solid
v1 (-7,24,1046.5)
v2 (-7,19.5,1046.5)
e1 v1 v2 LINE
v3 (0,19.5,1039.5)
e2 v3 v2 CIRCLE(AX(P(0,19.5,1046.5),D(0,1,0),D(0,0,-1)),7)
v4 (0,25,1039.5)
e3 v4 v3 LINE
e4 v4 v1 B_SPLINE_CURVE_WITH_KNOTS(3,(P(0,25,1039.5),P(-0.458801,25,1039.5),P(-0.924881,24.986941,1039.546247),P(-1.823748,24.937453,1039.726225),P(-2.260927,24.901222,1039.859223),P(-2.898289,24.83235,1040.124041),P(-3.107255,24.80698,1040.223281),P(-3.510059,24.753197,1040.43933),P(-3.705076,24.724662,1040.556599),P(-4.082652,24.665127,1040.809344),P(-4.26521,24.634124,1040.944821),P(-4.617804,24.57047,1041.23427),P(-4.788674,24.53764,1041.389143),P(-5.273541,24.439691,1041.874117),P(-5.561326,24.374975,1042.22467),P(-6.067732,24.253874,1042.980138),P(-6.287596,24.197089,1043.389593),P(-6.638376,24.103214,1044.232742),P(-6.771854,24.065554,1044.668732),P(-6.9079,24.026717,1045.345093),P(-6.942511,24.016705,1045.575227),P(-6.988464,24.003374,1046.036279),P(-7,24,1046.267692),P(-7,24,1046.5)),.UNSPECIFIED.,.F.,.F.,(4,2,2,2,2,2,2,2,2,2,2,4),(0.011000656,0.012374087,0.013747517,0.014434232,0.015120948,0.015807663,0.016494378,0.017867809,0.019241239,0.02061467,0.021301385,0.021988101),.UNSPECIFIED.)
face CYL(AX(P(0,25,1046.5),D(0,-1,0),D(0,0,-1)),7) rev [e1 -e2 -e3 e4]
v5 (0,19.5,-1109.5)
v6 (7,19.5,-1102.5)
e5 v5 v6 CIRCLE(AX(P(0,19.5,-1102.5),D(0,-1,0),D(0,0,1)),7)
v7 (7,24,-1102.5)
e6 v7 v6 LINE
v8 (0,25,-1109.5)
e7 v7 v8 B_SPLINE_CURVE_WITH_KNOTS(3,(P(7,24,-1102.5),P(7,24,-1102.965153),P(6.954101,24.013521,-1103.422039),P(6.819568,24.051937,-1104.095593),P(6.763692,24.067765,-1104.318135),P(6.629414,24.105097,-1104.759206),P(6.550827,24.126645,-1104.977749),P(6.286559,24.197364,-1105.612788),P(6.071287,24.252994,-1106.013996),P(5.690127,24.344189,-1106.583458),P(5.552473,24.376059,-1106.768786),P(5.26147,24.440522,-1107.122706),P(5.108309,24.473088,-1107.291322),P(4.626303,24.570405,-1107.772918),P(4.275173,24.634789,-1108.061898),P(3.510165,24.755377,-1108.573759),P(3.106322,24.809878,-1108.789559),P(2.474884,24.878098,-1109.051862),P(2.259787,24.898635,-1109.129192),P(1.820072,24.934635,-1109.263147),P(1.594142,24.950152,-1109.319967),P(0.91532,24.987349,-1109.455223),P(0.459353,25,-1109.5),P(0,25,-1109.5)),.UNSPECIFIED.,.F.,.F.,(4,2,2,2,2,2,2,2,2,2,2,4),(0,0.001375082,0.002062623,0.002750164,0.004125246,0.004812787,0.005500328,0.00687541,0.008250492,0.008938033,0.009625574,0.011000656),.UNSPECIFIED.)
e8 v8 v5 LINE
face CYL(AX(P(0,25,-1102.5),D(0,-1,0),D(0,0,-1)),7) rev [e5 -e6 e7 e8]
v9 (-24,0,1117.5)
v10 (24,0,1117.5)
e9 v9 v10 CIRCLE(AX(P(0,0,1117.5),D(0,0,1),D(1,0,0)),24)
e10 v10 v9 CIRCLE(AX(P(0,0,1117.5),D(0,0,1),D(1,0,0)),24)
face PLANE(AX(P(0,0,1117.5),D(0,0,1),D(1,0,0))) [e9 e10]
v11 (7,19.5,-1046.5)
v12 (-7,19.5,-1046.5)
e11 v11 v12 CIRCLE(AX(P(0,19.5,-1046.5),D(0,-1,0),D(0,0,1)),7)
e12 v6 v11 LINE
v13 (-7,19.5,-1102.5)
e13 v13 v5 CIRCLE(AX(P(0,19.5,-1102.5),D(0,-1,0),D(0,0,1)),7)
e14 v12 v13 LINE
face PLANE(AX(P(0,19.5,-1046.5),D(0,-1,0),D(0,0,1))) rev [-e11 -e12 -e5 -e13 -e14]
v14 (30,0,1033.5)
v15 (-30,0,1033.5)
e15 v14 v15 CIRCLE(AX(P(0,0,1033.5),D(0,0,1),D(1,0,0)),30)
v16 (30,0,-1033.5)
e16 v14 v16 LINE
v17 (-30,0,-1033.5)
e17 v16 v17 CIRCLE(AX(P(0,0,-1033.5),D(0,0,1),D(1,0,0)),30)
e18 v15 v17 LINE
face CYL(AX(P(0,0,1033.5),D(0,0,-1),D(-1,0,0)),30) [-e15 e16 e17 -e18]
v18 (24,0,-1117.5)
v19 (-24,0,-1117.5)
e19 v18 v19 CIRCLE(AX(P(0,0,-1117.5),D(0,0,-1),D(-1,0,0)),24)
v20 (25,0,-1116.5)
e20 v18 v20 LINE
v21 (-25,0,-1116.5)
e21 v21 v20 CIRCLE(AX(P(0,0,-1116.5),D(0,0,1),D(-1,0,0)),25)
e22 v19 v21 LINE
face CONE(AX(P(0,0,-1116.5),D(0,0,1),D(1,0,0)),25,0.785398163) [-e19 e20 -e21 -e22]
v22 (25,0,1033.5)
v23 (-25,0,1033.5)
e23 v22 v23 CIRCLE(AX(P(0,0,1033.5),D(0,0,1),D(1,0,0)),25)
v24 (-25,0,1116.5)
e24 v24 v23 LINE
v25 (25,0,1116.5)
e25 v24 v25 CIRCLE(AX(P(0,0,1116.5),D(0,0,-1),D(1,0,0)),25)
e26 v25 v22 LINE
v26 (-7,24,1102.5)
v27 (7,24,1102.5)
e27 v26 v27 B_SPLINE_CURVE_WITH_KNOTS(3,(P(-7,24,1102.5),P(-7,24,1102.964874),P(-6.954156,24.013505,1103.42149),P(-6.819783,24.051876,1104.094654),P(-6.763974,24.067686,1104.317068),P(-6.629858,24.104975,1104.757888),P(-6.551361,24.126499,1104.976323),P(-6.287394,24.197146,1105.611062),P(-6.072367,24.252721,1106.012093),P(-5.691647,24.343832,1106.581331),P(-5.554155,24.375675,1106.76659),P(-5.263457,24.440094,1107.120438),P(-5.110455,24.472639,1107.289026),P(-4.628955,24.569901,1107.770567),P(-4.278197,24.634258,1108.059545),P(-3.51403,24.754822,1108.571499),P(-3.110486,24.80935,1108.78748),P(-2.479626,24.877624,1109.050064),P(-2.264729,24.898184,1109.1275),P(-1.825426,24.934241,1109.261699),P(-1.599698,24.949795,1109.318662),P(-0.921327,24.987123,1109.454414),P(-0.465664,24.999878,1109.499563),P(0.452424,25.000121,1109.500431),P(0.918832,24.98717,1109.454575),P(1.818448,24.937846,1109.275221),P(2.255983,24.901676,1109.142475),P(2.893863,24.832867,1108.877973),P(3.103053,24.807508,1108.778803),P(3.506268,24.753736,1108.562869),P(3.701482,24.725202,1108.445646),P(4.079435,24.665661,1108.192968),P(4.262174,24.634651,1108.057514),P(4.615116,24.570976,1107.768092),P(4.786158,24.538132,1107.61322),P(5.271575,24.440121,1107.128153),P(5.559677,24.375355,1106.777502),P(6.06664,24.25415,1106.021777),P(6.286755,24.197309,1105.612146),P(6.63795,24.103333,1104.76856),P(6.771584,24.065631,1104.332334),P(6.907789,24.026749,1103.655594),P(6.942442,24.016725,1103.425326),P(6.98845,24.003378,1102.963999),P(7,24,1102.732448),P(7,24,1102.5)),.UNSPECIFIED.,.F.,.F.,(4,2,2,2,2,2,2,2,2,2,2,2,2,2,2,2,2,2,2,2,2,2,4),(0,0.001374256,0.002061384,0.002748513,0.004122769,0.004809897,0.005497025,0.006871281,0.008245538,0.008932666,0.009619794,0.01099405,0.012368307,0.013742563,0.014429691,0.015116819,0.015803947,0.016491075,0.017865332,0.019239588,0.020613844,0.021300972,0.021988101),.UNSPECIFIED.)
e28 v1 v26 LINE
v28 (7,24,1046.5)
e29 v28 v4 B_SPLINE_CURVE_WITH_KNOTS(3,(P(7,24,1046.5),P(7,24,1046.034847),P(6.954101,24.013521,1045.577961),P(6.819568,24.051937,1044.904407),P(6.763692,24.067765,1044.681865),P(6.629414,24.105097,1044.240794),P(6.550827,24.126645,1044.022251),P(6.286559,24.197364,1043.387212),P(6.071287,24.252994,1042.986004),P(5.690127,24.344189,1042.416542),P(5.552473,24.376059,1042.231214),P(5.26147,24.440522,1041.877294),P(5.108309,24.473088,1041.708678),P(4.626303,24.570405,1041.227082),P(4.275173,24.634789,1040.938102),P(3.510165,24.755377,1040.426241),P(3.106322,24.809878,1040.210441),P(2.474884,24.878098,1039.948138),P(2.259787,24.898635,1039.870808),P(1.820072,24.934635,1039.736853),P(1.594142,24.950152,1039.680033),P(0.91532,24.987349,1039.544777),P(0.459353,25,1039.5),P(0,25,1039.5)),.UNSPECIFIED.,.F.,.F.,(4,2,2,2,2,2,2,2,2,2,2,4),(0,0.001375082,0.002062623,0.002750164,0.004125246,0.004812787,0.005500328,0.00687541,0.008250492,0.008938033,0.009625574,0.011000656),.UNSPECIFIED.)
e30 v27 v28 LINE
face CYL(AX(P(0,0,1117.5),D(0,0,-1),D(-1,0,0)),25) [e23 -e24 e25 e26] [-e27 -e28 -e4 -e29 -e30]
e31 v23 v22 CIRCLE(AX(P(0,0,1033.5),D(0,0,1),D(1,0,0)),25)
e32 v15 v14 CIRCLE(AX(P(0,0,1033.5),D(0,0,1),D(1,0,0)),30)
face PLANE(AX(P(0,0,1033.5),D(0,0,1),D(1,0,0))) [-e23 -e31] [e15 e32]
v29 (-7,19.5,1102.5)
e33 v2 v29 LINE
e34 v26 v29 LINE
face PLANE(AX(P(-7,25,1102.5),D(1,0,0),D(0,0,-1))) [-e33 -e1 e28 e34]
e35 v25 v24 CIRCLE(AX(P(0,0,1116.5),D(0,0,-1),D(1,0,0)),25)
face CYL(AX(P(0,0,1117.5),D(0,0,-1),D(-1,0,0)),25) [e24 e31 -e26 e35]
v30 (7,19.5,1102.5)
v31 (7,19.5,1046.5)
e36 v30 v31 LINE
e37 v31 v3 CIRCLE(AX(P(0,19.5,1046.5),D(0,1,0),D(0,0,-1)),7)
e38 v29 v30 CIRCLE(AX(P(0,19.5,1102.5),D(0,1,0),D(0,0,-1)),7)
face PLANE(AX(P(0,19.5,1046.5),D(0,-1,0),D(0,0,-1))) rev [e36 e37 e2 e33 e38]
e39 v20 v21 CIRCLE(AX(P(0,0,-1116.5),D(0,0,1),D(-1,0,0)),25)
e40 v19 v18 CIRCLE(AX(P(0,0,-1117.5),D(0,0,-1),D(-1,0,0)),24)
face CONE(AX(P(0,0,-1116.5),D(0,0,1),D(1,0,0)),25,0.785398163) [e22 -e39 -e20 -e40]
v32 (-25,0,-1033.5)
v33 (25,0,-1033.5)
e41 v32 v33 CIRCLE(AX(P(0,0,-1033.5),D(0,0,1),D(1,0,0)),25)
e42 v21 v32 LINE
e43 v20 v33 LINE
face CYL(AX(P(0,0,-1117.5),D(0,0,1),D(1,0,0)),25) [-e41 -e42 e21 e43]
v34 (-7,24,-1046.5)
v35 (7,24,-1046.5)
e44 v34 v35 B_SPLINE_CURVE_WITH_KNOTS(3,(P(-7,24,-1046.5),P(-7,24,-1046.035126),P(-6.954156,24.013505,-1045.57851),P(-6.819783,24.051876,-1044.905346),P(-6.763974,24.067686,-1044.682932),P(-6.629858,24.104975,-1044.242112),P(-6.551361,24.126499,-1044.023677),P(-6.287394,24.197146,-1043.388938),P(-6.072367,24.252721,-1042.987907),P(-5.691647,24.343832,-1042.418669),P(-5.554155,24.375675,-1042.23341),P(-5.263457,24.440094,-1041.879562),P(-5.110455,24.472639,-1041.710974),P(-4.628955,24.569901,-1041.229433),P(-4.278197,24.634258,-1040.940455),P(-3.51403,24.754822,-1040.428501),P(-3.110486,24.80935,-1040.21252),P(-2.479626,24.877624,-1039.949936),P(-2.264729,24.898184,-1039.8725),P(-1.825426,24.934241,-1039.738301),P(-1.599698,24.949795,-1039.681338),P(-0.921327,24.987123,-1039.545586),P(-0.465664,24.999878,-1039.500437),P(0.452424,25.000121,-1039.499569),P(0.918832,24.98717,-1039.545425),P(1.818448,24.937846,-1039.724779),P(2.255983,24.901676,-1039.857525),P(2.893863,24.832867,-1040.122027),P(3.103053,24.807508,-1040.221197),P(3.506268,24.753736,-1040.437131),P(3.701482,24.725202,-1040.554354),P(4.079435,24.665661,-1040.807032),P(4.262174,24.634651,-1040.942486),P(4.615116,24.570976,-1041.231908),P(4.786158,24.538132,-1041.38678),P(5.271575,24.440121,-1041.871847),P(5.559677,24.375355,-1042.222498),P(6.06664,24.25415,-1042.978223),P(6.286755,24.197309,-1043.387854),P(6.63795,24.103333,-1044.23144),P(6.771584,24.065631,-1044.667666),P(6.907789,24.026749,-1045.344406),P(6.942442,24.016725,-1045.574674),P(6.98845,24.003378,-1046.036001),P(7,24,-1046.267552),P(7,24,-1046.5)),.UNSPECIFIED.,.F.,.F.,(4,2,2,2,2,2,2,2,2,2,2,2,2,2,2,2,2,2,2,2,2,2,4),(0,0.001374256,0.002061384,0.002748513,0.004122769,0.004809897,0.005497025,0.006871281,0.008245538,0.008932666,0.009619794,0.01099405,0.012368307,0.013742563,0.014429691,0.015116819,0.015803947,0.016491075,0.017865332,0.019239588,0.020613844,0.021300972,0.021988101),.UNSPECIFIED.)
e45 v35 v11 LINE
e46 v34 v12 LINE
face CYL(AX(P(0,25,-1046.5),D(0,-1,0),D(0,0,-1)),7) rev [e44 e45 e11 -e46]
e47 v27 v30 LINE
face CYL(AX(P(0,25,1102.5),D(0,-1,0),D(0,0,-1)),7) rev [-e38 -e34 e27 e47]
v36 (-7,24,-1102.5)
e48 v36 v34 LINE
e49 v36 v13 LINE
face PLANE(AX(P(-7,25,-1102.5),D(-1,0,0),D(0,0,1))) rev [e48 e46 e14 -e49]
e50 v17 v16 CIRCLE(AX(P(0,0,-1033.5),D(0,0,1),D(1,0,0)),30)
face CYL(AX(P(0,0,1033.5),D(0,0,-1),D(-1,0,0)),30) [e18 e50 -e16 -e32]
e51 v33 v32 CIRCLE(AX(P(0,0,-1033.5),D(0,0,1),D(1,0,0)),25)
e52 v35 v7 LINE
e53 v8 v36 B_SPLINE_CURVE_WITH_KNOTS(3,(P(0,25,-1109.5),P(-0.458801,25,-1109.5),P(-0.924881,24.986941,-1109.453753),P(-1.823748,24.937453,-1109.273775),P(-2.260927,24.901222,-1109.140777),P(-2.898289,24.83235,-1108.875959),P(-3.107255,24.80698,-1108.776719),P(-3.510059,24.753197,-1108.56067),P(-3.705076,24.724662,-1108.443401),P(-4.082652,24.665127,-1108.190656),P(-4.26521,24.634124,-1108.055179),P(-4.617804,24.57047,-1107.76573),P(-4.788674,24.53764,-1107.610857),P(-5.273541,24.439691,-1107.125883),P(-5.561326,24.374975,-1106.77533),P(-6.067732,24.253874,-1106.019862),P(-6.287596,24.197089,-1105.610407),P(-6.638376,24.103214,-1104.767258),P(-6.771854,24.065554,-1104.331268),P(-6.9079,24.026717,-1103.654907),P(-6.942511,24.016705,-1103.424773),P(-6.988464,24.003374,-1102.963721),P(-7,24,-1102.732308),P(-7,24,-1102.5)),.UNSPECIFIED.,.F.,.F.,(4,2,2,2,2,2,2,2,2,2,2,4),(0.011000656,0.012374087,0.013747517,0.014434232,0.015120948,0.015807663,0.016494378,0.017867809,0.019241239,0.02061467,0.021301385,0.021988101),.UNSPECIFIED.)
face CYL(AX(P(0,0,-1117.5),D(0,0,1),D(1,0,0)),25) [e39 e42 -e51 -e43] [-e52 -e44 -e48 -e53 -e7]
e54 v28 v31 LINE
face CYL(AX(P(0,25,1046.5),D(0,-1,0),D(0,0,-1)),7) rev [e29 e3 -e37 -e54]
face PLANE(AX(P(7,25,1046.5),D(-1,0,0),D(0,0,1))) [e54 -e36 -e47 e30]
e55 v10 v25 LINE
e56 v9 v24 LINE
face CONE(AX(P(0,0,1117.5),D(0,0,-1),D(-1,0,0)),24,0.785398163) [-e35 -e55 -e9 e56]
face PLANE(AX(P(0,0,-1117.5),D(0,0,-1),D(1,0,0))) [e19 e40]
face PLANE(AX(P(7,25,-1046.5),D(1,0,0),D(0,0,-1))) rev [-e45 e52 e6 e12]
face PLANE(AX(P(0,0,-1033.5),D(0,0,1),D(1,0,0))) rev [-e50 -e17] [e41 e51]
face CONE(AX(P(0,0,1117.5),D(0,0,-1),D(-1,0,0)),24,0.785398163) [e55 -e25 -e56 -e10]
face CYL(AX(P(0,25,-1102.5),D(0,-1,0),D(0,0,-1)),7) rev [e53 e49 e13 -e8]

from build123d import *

# Parameters (mm, degrees)
SKETCH1_R                = 30
EXTRUDE1_DEPTH           = 1033.5
SKETCH2_R                = 25
EXTRUDE2_DEPTH           = 84
CHAMFER1_SIZE            = 1
EXTRUDE3_DEPTH           = 5.5
CHAMFER1_OF_MIRROR1_SIZE = 1


with BuildPart() as part:
    # Sketch1 → Extrude1 (new, symmetric)
    with BuildSketch(Plane.XY):
        Circle(SKETCH1_R)
    extrude(amount=EXTRUDE1_DEPTH, both=True)

    # Sketch2 → Extrude2 (add)
    with BuildSketch(Plane.XY.offset(1033.5)):
        with Locations(Location((0, 0, 0), (0, 0, 180))):
            Circle(SKETCH2_R)
    extrude2 = extrude(amount=EXTRUDE2_DEPTH)

    # Chamfer1
    chamfer1_edges = [part.edges().sort_by_distance(p)[0] for p in [
        (25, 0, 1117.5),
    ]]
    chamfer(chamfer1_edges, length=CHAMFER1_SIZE)

    # Sketch3 → Extrude3 (cut)
    with BuildSketch(Plane(origin=(0, 19.5, 0), x_dir=(-1, 0, 0), z_dir=(0, 1, 0))):
        with BuildLine():
            Line((7, 1102.5), (7, 1046.5))
            ThreePointArc((7, 1046.5), (0, 1039.5), (-7, 1046.5))
            Line((-7, 1046.5), (-7, 1102.5))
            ThreePointArc((-7, 1102.5), (0, 1109.5), (7, 1102.5))
        make_face()
    extrude3 = extrude(amount=EXTRUDE3_DEPTH, mode=Mode.SUBTRACT)

    # Mirror1: Extrude2, Extrude3 across plane
    add(extrude2.mirror(Plane.XY))
    add(extrude3.mirror(Plane.XY), mode=Mode.SUBTRACT)

    # Chamfer1 of Mirror1
    chamfer1_of_mirror1_edges = [part.edges().sort_by_distance(p)[0] for p in [
        (25, 0, -1117.5),
    ]]
    chamfer(chamfer1_of_mirror1_edges, length=CHAMFER1_OF_MIRROR1_SIZE)


solid = part.part
